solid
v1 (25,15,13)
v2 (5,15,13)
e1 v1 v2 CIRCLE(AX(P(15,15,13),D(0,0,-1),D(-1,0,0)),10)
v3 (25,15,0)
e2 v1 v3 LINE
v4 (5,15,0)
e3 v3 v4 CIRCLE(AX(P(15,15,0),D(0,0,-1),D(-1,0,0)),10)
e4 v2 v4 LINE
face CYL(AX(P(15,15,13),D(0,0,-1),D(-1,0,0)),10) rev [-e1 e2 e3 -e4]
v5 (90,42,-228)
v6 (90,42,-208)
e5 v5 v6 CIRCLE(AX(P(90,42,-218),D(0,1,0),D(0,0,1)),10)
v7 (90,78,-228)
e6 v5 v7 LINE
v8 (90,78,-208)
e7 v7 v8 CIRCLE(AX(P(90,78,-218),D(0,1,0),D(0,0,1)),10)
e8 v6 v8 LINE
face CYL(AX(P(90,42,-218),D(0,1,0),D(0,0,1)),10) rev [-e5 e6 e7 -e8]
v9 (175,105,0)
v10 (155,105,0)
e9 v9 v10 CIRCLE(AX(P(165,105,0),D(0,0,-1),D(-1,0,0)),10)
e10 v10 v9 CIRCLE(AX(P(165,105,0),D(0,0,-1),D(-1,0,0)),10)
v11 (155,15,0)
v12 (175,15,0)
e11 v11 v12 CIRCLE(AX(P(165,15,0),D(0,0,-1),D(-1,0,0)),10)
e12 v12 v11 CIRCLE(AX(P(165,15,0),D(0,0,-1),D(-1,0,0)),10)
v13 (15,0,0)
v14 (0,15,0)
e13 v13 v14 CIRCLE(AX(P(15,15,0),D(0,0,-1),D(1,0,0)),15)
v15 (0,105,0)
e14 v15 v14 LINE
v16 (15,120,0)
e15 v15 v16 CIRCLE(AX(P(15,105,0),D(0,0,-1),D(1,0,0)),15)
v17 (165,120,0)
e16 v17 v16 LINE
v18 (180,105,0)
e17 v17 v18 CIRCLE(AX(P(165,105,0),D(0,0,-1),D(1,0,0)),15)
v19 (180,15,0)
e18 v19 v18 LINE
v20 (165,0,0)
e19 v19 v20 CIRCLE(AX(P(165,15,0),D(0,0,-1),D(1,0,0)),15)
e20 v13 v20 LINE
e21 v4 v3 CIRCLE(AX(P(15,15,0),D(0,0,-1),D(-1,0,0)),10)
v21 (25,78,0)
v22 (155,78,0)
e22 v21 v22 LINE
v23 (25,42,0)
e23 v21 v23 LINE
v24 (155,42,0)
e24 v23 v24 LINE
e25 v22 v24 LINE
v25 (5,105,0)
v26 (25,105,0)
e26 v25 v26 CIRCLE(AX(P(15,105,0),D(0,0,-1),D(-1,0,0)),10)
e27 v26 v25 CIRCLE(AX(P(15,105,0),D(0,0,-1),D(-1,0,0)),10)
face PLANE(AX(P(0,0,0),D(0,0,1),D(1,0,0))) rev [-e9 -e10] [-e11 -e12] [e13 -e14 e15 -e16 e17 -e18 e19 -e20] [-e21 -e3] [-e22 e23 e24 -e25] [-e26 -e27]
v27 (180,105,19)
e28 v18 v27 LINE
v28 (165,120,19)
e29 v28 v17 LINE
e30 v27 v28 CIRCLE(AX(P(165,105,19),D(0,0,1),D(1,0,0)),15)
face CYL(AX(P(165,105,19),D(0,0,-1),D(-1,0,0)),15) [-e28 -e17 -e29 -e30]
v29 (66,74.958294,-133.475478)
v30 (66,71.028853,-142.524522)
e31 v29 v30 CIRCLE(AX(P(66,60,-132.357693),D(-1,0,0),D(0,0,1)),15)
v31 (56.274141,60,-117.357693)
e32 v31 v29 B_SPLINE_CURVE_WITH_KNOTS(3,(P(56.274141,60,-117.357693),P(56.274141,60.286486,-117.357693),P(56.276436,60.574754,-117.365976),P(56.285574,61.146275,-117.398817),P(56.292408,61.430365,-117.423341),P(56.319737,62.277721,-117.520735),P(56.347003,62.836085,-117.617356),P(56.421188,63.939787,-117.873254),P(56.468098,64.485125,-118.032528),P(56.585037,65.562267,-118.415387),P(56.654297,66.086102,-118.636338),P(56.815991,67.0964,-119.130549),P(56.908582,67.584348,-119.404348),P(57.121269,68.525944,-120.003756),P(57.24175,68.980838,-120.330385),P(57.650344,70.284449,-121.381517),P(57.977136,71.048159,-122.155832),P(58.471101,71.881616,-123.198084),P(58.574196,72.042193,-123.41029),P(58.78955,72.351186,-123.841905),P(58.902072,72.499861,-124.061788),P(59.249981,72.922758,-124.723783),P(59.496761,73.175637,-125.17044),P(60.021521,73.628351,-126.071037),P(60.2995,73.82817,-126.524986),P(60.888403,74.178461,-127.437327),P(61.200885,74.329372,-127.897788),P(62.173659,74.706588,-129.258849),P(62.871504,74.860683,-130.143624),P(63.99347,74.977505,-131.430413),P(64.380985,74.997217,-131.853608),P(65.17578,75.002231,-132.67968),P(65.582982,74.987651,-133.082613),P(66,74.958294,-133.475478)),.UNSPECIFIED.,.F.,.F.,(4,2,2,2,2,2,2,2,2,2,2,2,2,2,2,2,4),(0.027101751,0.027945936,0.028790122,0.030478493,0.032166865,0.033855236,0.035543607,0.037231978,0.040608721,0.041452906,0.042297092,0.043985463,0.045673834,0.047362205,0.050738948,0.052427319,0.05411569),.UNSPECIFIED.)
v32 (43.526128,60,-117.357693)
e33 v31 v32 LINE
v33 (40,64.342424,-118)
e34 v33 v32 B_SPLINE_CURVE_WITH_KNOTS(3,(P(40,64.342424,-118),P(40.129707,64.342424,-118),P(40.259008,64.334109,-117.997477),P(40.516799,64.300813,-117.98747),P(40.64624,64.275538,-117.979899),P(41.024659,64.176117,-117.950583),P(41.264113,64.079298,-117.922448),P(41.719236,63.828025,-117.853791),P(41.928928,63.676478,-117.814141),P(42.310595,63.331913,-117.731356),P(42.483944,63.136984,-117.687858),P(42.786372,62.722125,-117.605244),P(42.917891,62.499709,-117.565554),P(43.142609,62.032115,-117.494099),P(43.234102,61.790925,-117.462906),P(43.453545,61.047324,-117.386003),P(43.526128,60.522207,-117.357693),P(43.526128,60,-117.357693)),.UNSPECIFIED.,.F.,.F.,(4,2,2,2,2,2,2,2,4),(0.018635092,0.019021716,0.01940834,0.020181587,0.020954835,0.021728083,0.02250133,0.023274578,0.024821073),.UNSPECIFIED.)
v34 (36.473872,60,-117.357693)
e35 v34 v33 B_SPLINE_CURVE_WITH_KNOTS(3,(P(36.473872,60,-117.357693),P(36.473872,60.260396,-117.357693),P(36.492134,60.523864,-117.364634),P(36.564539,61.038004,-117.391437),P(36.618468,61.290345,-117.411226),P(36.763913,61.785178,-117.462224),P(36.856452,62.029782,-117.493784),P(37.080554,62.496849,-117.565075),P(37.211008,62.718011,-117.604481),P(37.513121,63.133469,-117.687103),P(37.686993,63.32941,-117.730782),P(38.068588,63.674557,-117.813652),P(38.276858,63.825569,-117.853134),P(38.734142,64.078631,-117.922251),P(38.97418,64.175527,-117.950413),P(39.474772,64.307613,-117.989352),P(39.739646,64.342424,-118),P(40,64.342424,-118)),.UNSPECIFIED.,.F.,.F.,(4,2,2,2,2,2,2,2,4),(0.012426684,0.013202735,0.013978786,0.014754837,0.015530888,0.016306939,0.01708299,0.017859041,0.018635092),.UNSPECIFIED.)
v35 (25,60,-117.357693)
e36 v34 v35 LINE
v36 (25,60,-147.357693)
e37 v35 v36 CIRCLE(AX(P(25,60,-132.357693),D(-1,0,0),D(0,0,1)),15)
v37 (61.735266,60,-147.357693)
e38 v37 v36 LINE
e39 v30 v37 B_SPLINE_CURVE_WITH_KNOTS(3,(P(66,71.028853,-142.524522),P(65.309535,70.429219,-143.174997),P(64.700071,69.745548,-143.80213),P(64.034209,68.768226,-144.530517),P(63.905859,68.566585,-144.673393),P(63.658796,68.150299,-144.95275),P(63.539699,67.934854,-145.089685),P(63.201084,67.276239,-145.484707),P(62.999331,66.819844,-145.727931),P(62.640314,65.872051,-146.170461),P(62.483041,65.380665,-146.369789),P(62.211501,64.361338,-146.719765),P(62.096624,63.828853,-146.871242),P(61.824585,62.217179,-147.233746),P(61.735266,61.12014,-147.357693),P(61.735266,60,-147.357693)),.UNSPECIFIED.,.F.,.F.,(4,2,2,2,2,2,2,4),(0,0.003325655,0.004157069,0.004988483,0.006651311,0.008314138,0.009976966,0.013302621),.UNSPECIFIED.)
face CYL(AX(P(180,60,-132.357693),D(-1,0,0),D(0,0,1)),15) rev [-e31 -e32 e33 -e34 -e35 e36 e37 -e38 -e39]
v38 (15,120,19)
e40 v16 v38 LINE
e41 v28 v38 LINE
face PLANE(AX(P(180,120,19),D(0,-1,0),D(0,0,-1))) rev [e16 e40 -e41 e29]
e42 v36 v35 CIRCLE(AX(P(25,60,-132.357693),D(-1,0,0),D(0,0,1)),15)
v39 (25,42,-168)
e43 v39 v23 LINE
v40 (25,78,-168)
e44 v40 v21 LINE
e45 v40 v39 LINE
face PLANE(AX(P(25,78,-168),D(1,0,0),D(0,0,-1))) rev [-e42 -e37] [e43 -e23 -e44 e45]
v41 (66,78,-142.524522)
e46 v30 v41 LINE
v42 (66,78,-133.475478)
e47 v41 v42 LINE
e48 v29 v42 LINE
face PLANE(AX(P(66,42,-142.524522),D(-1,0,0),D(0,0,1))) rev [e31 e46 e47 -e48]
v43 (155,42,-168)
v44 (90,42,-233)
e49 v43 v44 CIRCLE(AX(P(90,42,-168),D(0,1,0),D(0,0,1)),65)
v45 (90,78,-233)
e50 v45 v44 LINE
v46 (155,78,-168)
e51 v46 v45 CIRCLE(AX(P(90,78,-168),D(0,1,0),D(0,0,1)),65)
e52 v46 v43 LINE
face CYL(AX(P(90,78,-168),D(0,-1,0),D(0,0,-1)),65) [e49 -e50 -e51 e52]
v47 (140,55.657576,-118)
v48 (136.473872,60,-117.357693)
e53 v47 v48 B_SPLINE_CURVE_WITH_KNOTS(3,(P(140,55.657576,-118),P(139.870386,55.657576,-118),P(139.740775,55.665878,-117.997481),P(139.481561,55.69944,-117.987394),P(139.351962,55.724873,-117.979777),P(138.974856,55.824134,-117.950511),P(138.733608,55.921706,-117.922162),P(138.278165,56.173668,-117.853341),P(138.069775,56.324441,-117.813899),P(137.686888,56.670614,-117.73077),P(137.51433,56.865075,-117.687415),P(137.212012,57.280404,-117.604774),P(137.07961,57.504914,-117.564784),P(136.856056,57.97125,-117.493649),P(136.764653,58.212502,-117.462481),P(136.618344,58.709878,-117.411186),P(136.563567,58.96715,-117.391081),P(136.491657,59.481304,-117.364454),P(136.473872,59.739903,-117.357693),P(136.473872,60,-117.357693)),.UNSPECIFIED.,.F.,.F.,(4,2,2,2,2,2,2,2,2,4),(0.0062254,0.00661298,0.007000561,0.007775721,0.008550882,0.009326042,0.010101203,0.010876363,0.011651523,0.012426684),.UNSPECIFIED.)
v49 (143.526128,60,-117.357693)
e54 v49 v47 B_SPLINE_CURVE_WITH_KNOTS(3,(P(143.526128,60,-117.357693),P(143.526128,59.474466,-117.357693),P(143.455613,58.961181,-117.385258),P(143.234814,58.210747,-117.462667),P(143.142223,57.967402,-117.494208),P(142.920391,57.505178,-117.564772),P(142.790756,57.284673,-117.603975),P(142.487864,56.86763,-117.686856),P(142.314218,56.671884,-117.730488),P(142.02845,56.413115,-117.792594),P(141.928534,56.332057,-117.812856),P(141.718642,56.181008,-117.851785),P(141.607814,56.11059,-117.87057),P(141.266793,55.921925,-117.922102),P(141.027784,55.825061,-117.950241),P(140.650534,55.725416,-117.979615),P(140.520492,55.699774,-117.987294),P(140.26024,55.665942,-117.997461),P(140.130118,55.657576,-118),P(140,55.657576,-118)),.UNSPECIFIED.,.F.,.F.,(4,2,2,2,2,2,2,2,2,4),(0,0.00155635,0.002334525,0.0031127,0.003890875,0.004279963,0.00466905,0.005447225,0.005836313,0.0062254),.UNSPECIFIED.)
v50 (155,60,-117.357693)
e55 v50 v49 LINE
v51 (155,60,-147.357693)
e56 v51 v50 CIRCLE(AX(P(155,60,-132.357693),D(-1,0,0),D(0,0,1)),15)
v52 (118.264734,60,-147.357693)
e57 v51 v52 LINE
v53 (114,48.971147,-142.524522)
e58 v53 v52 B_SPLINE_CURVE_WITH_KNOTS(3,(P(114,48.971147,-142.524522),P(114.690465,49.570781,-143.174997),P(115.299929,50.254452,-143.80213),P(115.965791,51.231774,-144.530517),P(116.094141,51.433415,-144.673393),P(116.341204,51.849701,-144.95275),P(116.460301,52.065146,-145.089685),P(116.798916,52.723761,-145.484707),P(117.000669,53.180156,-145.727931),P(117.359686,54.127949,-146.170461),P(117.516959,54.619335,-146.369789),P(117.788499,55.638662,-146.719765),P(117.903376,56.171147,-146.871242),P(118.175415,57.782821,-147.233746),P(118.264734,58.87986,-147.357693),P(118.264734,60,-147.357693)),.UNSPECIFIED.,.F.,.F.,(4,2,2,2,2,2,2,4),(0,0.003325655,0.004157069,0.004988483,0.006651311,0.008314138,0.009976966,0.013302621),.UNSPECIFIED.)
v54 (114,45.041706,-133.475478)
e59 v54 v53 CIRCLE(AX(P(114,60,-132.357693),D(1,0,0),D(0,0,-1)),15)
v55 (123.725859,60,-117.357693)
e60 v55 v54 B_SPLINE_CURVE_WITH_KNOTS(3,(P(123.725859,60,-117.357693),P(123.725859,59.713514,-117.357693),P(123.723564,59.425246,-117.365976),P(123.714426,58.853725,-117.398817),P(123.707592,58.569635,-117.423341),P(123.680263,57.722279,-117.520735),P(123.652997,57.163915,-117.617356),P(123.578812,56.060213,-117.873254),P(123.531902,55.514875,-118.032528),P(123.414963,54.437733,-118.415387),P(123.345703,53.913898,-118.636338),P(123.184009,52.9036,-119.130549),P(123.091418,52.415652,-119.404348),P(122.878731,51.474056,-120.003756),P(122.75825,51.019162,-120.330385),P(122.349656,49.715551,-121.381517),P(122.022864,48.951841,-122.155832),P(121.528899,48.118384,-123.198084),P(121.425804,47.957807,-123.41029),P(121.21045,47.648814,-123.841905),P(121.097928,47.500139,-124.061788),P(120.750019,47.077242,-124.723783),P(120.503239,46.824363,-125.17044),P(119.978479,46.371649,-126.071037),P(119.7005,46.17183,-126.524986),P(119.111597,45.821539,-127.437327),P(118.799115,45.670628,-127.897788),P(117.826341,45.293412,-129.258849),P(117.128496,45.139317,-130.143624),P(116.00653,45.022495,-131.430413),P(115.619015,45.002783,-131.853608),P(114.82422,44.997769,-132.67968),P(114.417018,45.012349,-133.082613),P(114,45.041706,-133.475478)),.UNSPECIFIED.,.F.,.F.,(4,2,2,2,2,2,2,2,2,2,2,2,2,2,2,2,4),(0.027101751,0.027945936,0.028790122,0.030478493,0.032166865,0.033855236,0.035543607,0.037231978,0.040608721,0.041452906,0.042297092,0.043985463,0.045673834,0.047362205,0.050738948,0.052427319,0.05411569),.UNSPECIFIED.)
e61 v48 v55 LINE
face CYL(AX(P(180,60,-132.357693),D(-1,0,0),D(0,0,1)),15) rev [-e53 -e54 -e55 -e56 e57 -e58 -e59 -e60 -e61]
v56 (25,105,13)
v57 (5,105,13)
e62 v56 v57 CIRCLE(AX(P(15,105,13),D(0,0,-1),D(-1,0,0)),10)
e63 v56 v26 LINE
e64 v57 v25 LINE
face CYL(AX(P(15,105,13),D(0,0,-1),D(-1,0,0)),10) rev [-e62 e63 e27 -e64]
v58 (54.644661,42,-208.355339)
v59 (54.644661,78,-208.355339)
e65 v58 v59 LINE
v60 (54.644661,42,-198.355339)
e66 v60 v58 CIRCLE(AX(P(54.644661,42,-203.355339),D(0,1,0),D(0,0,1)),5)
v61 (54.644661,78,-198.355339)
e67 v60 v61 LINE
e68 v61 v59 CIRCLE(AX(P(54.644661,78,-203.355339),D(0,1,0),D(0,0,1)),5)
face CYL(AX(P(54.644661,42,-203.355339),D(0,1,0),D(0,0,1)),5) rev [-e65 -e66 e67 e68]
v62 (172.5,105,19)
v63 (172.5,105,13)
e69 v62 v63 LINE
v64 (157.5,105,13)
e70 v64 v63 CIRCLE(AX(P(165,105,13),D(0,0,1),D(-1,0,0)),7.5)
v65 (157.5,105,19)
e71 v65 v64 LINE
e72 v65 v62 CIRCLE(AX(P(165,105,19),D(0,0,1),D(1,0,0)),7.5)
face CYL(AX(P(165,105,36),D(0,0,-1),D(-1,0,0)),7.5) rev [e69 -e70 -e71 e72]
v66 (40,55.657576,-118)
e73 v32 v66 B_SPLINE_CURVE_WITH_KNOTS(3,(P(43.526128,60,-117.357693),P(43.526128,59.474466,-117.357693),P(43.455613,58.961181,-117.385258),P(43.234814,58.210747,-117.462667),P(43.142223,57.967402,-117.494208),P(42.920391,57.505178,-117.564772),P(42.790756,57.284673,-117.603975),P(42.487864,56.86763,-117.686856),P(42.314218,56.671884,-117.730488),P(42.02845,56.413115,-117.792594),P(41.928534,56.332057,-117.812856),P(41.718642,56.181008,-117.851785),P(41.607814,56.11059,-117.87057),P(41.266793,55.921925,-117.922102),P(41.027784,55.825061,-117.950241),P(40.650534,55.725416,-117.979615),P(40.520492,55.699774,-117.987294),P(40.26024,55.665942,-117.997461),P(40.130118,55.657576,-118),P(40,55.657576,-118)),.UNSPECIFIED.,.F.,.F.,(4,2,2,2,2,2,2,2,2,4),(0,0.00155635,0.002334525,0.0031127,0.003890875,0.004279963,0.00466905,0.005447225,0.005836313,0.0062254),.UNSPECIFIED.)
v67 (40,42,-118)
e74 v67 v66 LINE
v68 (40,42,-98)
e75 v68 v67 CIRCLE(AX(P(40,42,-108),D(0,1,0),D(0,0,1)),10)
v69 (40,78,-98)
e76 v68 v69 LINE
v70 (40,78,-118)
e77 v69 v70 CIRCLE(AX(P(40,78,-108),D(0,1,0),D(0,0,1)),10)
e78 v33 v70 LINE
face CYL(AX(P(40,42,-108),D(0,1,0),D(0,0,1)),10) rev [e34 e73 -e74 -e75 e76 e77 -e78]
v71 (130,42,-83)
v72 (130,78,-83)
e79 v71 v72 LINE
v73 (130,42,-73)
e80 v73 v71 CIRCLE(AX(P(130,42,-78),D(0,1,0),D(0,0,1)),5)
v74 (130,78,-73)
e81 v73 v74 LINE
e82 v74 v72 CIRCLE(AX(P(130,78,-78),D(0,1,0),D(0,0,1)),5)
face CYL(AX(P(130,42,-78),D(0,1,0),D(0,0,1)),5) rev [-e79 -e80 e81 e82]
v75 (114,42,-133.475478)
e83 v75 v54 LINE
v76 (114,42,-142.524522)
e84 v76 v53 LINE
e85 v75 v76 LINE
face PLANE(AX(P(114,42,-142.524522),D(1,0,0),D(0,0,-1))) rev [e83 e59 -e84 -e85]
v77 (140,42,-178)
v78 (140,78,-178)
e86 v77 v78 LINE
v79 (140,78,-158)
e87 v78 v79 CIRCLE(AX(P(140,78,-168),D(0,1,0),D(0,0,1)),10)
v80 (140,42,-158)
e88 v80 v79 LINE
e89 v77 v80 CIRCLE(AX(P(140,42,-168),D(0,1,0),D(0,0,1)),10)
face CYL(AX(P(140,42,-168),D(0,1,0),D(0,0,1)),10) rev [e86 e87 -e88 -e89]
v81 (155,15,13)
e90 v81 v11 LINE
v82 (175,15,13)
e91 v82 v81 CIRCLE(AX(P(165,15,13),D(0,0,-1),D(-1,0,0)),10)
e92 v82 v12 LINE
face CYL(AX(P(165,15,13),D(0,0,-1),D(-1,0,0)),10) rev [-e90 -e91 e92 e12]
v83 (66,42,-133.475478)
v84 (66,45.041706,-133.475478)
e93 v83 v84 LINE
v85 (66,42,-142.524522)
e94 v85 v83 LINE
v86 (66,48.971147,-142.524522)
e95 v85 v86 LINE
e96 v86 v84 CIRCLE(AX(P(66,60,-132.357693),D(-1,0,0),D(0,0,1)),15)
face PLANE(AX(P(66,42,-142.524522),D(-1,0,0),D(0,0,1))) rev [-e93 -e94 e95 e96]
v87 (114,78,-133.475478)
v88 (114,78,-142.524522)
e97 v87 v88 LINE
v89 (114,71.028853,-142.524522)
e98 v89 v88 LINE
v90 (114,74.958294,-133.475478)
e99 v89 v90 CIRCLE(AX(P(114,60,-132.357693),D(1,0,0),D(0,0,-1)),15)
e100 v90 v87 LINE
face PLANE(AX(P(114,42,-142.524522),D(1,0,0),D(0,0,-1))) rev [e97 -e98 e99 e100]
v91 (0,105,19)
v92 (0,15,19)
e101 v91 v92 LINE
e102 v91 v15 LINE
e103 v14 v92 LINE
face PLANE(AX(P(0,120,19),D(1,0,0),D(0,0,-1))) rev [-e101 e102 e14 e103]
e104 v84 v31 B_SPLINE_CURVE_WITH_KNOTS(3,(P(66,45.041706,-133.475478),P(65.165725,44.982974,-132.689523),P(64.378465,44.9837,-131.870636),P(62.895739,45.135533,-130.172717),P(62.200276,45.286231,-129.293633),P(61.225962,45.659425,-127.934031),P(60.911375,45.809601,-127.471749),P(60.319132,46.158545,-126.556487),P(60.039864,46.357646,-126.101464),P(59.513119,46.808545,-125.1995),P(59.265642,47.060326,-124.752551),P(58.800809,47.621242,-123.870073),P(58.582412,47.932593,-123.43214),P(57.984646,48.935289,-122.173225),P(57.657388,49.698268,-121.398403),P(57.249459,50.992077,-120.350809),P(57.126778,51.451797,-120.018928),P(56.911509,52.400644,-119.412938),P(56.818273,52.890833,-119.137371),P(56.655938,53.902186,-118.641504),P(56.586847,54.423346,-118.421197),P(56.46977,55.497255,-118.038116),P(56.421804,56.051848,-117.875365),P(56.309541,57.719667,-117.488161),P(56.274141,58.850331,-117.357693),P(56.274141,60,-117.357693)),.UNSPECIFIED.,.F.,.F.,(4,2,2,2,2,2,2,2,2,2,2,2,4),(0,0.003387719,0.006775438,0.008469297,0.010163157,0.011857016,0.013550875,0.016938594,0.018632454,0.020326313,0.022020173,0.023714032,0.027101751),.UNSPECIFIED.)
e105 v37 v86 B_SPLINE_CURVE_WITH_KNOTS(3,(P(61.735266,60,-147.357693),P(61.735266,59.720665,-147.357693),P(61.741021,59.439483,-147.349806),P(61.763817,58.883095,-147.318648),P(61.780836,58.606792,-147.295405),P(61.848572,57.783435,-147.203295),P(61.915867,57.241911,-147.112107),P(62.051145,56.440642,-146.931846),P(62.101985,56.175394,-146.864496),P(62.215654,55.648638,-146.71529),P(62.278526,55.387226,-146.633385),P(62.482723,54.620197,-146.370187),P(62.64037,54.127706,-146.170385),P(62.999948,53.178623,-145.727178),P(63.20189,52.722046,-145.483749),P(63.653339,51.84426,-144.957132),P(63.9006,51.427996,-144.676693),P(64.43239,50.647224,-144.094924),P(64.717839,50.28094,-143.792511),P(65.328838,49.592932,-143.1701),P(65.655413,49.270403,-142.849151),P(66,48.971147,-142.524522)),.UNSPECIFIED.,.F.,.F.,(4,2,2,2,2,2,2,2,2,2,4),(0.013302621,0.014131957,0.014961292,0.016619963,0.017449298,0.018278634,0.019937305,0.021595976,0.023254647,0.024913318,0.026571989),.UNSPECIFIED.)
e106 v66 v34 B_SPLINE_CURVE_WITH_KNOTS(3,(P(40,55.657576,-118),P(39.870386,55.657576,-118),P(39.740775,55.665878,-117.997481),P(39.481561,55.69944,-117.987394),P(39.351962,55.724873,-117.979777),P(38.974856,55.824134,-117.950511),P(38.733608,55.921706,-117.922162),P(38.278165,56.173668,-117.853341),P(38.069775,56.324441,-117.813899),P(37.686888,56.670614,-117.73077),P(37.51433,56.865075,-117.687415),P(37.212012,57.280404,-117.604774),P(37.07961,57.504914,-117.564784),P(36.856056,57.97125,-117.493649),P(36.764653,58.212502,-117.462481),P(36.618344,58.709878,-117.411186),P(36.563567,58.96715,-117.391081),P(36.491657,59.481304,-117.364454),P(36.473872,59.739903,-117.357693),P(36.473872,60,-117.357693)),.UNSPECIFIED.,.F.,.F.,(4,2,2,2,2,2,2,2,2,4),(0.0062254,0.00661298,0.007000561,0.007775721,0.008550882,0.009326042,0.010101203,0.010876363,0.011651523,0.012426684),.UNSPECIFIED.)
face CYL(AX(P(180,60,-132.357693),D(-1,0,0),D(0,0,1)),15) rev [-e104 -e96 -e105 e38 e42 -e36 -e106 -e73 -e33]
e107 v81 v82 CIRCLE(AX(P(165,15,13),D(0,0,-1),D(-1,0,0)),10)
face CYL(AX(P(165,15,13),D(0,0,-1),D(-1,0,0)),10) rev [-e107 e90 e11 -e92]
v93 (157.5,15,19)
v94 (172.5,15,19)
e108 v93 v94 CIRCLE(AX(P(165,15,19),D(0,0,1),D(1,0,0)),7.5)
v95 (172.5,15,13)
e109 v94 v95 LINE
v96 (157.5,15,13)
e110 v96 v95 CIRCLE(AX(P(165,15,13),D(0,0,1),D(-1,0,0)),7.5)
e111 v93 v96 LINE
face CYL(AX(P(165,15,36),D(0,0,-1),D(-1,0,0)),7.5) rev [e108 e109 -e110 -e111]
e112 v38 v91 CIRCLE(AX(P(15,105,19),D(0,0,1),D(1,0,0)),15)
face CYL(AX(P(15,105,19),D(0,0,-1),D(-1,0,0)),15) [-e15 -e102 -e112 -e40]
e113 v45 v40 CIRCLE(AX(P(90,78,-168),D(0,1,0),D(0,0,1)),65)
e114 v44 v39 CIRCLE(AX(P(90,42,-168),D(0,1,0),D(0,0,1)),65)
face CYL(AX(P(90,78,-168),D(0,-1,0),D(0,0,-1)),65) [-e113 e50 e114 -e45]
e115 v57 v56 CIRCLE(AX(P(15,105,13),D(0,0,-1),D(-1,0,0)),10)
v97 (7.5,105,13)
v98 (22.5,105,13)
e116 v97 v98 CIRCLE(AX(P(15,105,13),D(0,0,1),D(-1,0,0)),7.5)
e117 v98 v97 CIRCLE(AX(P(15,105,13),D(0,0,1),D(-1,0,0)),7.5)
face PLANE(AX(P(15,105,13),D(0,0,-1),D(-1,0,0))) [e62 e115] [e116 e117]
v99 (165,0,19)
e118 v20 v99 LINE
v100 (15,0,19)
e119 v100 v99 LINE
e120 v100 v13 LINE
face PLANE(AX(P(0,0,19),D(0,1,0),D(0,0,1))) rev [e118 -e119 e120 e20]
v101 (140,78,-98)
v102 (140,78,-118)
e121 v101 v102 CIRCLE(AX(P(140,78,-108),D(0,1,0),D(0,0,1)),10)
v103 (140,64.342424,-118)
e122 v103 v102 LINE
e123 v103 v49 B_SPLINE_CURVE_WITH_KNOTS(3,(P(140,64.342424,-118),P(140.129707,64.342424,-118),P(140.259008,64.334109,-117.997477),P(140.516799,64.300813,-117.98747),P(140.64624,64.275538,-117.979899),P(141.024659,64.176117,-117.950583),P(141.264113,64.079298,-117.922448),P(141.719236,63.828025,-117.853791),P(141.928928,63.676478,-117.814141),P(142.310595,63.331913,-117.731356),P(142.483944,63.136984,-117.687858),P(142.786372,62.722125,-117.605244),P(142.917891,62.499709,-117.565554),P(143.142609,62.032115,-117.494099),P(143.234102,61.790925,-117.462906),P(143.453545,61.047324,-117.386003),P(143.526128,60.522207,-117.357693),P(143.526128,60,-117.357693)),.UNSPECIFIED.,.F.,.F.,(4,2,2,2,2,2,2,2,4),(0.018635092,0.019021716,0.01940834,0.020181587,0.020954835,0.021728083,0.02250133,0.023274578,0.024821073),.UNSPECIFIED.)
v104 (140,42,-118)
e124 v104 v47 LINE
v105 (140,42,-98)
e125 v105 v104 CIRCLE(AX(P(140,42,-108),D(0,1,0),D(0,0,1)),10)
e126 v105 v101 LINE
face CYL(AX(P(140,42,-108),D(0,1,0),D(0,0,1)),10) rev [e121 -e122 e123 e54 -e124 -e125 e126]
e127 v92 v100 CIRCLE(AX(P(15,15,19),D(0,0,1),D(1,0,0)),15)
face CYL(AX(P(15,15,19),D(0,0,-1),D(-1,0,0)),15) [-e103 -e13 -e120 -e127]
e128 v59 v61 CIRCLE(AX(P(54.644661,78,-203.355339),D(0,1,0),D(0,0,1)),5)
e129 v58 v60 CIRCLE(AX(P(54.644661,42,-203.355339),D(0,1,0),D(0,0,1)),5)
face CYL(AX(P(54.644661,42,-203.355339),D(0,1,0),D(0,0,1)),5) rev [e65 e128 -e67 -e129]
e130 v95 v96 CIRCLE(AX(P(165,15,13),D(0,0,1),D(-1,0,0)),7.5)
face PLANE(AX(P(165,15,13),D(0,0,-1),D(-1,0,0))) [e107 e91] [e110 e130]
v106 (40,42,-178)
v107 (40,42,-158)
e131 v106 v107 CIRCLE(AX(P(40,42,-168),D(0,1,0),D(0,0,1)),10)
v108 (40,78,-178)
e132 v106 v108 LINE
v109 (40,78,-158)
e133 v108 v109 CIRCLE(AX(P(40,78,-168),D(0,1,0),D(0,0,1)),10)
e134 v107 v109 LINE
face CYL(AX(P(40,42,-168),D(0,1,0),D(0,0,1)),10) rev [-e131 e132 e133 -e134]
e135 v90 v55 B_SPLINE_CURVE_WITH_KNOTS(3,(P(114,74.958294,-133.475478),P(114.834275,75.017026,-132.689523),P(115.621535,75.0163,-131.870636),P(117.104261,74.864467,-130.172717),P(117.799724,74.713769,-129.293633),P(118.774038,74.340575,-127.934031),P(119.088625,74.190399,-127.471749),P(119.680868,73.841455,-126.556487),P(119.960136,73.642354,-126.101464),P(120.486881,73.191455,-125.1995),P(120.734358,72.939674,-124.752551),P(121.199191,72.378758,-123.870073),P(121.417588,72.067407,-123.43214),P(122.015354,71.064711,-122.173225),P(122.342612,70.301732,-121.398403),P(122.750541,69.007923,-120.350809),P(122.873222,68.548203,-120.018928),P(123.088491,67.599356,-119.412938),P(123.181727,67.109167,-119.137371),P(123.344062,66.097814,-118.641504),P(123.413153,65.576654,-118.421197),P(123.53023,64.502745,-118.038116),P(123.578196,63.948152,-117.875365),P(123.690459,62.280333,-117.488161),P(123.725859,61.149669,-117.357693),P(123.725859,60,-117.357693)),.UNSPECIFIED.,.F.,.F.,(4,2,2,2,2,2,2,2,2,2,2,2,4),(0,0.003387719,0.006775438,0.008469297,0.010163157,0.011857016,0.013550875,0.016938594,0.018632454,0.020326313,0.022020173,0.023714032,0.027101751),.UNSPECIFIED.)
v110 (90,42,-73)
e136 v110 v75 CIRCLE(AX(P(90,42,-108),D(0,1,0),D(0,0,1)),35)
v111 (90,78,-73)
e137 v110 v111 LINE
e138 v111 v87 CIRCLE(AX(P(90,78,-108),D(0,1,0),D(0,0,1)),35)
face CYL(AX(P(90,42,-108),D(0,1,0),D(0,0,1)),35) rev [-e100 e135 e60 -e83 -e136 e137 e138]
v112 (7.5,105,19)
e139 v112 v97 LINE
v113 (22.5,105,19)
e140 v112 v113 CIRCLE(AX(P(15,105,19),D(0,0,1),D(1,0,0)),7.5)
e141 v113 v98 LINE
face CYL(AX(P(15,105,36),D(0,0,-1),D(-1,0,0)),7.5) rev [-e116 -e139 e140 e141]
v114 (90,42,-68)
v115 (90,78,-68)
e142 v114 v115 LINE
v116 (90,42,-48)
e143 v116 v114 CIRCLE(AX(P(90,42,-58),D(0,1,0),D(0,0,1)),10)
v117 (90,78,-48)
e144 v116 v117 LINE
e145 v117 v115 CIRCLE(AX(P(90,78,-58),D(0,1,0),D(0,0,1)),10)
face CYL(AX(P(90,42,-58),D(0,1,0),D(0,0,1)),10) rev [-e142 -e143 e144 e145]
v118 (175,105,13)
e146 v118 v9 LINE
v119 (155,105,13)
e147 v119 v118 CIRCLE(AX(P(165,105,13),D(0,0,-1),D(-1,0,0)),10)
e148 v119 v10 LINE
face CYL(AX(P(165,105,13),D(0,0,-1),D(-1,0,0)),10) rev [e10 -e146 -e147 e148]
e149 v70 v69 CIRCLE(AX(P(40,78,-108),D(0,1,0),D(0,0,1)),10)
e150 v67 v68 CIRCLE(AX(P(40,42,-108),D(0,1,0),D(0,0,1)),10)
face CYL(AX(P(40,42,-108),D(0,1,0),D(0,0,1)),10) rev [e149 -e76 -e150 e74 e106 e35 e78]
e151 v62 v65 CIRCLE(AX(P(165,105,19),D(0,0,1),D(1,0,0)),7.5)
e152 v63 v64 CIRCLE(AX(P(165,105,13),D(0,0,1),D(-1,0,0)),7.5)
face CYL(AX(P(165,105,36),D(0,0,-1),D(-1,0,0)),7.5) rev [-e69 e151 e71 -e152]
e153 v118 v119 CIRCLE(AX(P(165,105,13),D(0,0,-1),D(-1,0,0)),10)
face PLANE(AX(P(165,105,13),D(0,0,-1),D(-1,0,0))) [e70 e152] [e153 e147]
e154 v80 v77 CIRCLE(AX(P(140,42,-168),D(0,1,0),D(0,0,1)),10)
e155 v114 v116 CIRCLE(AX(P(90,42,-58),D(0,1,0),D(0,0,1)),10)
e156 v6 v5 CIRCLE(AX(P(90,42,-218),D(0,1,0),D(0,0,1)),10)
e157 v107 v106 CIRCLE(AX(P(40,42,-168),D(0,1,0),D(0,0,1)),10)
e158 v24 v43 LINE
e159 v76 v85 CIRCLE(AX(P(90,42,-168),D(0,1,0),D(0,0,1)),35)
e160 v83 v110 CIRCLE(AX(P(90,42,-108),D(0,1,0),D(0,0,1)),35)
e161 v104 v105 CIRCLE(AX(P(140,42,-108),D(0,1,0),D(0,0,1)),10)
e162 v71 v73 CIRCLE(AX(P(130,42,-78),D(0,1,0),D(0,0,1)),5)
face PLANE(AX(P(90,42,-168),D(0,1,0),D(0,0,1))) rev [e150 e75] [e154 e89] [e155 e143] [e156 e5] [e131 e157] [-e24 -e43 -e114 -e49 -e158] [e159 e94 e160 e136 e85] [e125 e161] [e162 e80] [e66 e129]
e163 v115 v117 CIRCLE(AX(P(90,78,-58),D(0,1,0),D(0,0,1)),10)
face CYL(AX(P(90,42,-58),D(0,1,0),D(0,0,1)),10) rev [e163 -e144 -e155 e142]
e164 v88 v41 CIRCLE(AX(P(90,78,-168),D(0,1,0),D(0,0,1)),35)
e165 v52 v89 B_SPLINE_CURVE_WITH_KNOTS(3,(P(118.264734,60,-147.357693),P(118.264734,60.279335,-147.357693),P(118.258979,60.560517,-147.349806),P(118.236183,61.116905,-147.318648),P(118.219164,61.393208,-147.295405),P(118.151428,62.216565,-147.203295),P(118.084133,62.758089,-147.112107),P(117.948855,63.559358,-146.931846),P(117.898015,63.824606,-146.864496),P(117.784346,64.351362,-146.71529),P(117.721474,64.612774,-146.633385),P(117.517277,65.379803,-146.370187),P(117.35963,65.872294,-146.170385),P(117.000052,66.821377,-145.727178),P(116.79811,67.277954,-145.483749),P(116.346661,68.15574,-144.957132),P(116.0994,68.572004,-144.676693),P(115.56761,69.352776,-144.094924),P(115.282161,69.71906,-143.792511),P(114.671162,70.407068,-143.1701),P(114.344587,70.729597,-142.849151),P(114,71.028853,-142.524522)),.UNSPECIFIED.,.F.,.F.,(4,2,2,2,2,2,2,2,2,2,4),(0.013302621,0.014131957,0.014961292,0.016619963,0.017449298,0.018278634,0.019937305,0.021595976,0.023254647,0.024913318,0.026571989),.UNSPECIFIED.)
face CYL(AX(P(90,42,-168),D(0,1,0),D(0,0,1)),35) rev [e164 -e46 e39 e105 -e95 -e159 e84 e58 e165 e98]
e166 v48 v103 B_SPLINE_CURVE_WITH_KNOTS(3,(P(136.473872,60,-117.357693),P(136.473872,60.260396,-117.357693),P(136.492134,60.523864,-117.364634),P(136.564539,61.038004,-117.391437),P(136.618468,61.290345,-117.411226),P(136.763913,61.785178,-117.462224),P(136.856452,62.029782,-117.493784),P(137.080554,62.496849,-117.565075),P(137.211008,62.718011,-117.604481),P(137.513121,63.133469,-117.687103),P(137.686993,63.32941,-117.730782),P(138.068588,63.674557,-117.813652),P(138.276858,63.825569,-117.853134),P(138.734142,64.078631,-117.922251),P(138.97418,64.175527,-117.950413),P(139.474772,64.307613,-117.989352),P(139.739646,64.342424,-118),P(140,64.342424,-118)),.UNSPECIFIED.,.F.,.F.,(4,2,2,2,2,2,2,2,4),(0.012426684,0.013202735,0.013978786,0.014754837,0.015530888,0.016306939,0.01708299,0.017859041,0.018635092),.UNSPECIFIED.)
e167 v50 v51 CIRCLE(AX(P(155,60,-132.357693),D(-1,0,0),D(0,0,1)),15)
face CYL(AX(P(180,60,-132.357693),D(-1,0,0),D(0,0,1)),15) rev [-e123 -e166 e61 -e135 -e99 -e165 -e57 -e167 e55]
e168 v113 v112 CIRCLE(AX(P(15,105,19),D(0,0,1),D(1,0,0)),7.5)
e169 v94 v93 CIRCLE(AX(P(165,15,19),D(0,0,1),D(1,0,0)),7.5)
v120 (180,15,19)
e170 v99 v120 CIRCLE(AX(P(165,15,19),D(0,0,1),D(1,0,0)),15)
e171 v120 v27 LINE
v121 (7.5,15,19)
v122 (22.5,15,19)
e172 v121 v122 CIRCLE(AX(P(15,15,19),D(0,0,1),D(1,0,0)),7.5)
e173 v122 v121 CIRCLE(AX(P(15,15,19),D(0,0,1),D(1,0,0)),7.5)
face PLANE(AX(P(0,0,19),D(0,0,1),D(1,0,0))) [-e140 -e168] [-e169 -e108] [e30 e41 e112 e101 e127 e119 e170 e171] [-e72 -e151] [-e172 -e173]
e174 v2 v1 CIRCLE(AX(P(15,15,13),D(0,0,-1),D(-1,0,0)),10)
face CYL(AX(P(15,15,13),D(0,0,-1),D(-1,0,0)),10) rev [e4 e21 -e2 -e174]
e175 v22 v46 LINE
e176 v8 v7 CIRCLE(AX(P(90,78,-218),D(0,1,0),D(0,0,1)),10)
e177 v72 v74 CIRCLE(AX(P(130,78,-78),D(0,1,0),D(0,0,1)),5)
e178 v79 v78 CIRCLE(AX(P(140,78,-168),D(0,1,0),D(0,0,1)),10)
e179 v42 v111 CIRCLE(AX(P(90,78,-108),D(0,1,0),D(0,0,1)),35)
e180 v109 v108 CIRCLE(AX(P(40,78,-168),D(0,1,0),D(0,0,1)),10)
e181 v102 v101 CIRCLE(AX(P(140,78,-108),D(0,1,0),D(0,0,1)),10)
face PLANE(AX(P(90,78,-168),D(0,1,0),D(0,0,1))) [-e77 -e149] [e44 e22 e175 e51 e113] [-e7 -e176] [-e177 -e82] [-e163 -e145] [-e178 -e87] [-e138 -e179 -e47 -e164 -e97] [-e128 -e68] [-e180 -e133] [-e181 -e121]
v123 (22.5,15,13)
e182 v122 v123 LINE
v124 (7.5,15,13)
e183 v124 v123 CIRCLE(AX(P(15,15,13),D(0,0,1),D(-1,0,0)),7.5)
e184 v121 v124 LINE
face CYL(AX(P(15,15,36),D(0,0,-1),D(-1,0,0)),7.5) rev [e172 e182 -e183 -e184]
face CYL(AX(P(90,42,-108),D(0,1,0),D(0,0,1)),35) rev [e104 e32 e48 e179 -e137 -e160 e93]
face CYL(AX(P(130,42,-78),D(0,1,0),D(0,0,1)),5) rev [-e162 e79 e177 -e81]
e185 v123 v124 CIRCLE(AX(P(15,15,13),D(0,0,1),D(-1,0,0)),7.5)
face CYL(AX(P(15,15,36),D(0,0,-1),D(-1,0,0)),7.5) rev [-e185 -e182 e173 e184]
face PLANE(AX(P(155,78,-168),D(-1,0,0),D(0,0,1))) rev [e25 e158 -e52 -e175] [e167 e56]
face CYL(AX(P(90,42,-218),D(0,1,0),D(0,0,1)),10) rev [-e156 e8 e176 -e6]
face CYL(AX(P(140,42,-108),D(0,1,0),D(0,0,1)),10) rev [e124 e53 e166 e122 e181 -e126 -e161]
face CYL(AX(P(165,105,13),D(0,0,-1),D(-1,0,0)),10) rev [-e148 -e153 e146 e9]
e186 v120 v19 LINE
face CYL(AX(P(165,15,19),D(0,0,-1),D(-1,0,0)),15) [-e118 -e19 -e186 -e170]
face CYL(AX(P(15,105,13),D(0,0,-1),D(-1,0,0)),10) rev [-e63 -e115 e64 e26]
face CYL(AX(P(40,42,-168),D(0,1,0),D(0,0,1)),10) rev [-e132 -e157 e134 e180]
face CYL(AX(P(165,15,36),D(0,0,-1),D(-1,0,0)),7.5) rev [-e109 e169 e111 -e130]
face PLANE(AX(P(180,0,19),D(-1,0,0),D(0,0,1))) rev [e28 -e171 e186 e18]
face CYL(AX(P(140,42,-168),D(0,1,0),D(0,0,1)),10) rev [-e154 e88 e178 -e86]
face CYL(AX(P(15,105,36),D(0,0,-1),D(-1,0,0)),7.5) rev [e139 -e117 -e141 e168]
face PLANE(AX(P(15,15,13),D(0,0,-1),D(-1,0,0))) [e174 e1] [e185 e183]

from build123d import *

# Parameters (mm, degrees)
FLANGE_PROFILE_SKETCH_W                = 180
FLANGE_PROFILE_SKETCH_H                = 120
MOUNTING_FLANGE_DEPTH                  = 19
SUPPORT_ARM_DEPTH                      = 18
BEARING_BORE_AND_BOLT_HOLES_SKETCH_R   = 10
BEARING_BORE_AND_BOLT_HOLES_SKETCH_R_2 = 5
BEARING_BORE_AND_BOLT_HOLES_DEPTH      = 36
CROSS_HOLE_SKETCH_R                    = 15
CROSS_HOLE_30_DEPTH                    = 305.489737101
FLANGE_CORNER_FILLETS_R15_R            = 15
FLANGE_MOUNTING_HOLES_SKETCH_R         = 7.5
FLANGE_MOUNTING_HOLES_DEPTH            = 36
FLANGE_SECONDARY_CUT_SKETCH_R          = 10
FLANGE_SECONDARY_CUT_DEPTH             = 13


with BuildPart() as part:
    # Flange Profile Sketch → Mounting Flange (new body)
    with BuildSketch(Plane.XY):
        with Locations((90, 60)):
            Rectangle(FLANGE_PROFILE_SKETCH_W, FLANGE_PROFILE_SKETCH_H)
    extrude(amount=MOUNTING_FLANGE_DEPTH)

    # Support Arm Profile Sketch → Support Arm (add, symmetric)
    with BuildSketch(Plane(origin=(0, 60, 0), x_dir=(1, 0, 0), z_dir=(0, 1, 0))):
        with BuildLine():
            Line((25, 168), (25, 0))
            Line((25, 0), (155, 0))
            Line((155, 0), (155, 168))
            ThreePointArc((155, 168), (90, 233), (25, 168))
        make_face()
    extrude(amount=SUPPORT_ARM_DEPTH, both=True)

    # Bearing Bore and Bolt Holes Sketch → Bearing Bore and Bolt Holes (cut)
    with BuildSketch(Plane(origin=(0, 78, 0), x_dir=(1, 0, 0), z_dir=(0, 1, 0))):
        with Locations(Location((90, 218, 0), (0, 0, 270))):
            Circle(BEARING_BORE_AND_BOLT_HOLES_SKETCH_R)
        with Locations(Location((140, 168, 0), (0, 0, 270))):
            Circle(BEARING_BORE_AND_BOLT_HOLES_SKETCH_R)
        with Locations(Location((40, 168, 0), (0, 0, 270))):
            Circle(BEARING_BORE_AND_BOLT_HOLES_SKETCH_R)
        with Locations(Location((90, 58, 0), (0, 0, 270))):
            Circle(BEARING_BORE_AND_BOLT_HOLES_SKETCH_R)
        with Locations(Location((40, 108, 0), (0, 0, 270))):
            Circle(BEARING_BORE_AND_BOLT_HOLES_SKETCH_R)
        with Locations(Location((140, 108, 0), (0, 0, 270))):
            Circle(BEARING_BORE_AND_BOLT_HOLES_SKETCH_R)
        with Locations(Location((54.644660941, 203.355339059, 0), (0, 0, 270))):
            Circle(BEARING_BORE_AND_BOLT_HOLES_SKETCH_R_2)
        with Locations(Location((130, 78, 0), (0, 0, 270))):
            Circle(BEARING_BORE_AND_BOLT_HOLES_SKETCH_R_2)
        with BuildLine():
            Line((66, 142.524521594), (66, 133.475478406))
            ThreePointArc((66, 133.475478406), (90, 73), (114, 133.475478406))
            Line((114, 133.475478406), (114, 142.524521594))
            ThreePointArc((114, 142.524521594), (90, 203), (66, 142.524521594))
        make_face()
    extrude(amount=-BEARING_BORE_AND_BOLT_HOLES_DEPTH, mode=Mode.SUBTRACT)

    # Cross Hole Sketch → Cross Hole Ø30 (cut, through all)
    with BuildSketch(Plane.ZY.offset(-25)):
        with Locations((-132.357693154, 60)):
            Circle(CROSS_HOLE_SKETCH_R)
    extrude(amount=-CROSS_HOLE_30_DEPTH, mode=Mode.SUBTRACT)

    # Flange Corner Fillets R15
    flange_corner_fillets_r15_edges = [part.edges().sort_by_distance(p)[0] for p in [
        (0, 120, 9.5),
        (180, 120, 9.5),
        (180, 0, 9.5),
        (0, 0, 9.5),
    ]]
    fillet(flange_corner_fillets_r15_edges, radius=FLANGE_CORNER_FILLETS_R15_R)

    # Flange Mounting Holes Sketch → Flange Mounting Holes (cut)
    with BuildSketch(Plane(origin=(0, 0, 0), x_dir=(-1, 0, 0), z_dir=(0, 0, -1))):
        with Locations((-165, 15)):
            Circle(FLANGE_MOUNTING_HOLES_SKETCH_R)
        with Locations((-15, 15)):
            Circle(FLANGE_MOUNTING_HOLES_SKETCH_R)
        with Locations((-15, 105)):
            Circle(FLANGE_MOUNTING_HOLES_SKETCH_R)
        with Locations((-165, 105)):
            Circle(FLANGE_MOUNTING_HOLES_SKETCH_R)
    extrude(amount=-FLANGE_MOUNTING_HOLES_DEPTH, mode=Mode.SUBTRACT)

    # Flange Secondary Cut Sketch → Flange Secondary Cut (cut)
    with BuildSketch(Plane(origin=(0, 0, 0), x_dir=(-1, 0, 0), z_dir=(0, 0, -1))):
        with Locations((-165, 105)):
            Circle(FLANGE_SECONDARY_CUT_SKETCH_R)
        with Locations((-15, 105)):
            Circle(FLANGE_SECONDARY_CUT_SKETCH_R)
        with Locations((-15, 15)):
            Circle(FLANGE_SECONDARY_CUT_SKETCH_R)
        with Locations((-165, 15)):
            Circle(FLANGE_SECONDARY_CUT_SKETCH_R)
    extrude(amount=-FLANGE_SECONDARY_CUT_DEPTH, mode=Mode.SUBTRACT)


solid = part.part
